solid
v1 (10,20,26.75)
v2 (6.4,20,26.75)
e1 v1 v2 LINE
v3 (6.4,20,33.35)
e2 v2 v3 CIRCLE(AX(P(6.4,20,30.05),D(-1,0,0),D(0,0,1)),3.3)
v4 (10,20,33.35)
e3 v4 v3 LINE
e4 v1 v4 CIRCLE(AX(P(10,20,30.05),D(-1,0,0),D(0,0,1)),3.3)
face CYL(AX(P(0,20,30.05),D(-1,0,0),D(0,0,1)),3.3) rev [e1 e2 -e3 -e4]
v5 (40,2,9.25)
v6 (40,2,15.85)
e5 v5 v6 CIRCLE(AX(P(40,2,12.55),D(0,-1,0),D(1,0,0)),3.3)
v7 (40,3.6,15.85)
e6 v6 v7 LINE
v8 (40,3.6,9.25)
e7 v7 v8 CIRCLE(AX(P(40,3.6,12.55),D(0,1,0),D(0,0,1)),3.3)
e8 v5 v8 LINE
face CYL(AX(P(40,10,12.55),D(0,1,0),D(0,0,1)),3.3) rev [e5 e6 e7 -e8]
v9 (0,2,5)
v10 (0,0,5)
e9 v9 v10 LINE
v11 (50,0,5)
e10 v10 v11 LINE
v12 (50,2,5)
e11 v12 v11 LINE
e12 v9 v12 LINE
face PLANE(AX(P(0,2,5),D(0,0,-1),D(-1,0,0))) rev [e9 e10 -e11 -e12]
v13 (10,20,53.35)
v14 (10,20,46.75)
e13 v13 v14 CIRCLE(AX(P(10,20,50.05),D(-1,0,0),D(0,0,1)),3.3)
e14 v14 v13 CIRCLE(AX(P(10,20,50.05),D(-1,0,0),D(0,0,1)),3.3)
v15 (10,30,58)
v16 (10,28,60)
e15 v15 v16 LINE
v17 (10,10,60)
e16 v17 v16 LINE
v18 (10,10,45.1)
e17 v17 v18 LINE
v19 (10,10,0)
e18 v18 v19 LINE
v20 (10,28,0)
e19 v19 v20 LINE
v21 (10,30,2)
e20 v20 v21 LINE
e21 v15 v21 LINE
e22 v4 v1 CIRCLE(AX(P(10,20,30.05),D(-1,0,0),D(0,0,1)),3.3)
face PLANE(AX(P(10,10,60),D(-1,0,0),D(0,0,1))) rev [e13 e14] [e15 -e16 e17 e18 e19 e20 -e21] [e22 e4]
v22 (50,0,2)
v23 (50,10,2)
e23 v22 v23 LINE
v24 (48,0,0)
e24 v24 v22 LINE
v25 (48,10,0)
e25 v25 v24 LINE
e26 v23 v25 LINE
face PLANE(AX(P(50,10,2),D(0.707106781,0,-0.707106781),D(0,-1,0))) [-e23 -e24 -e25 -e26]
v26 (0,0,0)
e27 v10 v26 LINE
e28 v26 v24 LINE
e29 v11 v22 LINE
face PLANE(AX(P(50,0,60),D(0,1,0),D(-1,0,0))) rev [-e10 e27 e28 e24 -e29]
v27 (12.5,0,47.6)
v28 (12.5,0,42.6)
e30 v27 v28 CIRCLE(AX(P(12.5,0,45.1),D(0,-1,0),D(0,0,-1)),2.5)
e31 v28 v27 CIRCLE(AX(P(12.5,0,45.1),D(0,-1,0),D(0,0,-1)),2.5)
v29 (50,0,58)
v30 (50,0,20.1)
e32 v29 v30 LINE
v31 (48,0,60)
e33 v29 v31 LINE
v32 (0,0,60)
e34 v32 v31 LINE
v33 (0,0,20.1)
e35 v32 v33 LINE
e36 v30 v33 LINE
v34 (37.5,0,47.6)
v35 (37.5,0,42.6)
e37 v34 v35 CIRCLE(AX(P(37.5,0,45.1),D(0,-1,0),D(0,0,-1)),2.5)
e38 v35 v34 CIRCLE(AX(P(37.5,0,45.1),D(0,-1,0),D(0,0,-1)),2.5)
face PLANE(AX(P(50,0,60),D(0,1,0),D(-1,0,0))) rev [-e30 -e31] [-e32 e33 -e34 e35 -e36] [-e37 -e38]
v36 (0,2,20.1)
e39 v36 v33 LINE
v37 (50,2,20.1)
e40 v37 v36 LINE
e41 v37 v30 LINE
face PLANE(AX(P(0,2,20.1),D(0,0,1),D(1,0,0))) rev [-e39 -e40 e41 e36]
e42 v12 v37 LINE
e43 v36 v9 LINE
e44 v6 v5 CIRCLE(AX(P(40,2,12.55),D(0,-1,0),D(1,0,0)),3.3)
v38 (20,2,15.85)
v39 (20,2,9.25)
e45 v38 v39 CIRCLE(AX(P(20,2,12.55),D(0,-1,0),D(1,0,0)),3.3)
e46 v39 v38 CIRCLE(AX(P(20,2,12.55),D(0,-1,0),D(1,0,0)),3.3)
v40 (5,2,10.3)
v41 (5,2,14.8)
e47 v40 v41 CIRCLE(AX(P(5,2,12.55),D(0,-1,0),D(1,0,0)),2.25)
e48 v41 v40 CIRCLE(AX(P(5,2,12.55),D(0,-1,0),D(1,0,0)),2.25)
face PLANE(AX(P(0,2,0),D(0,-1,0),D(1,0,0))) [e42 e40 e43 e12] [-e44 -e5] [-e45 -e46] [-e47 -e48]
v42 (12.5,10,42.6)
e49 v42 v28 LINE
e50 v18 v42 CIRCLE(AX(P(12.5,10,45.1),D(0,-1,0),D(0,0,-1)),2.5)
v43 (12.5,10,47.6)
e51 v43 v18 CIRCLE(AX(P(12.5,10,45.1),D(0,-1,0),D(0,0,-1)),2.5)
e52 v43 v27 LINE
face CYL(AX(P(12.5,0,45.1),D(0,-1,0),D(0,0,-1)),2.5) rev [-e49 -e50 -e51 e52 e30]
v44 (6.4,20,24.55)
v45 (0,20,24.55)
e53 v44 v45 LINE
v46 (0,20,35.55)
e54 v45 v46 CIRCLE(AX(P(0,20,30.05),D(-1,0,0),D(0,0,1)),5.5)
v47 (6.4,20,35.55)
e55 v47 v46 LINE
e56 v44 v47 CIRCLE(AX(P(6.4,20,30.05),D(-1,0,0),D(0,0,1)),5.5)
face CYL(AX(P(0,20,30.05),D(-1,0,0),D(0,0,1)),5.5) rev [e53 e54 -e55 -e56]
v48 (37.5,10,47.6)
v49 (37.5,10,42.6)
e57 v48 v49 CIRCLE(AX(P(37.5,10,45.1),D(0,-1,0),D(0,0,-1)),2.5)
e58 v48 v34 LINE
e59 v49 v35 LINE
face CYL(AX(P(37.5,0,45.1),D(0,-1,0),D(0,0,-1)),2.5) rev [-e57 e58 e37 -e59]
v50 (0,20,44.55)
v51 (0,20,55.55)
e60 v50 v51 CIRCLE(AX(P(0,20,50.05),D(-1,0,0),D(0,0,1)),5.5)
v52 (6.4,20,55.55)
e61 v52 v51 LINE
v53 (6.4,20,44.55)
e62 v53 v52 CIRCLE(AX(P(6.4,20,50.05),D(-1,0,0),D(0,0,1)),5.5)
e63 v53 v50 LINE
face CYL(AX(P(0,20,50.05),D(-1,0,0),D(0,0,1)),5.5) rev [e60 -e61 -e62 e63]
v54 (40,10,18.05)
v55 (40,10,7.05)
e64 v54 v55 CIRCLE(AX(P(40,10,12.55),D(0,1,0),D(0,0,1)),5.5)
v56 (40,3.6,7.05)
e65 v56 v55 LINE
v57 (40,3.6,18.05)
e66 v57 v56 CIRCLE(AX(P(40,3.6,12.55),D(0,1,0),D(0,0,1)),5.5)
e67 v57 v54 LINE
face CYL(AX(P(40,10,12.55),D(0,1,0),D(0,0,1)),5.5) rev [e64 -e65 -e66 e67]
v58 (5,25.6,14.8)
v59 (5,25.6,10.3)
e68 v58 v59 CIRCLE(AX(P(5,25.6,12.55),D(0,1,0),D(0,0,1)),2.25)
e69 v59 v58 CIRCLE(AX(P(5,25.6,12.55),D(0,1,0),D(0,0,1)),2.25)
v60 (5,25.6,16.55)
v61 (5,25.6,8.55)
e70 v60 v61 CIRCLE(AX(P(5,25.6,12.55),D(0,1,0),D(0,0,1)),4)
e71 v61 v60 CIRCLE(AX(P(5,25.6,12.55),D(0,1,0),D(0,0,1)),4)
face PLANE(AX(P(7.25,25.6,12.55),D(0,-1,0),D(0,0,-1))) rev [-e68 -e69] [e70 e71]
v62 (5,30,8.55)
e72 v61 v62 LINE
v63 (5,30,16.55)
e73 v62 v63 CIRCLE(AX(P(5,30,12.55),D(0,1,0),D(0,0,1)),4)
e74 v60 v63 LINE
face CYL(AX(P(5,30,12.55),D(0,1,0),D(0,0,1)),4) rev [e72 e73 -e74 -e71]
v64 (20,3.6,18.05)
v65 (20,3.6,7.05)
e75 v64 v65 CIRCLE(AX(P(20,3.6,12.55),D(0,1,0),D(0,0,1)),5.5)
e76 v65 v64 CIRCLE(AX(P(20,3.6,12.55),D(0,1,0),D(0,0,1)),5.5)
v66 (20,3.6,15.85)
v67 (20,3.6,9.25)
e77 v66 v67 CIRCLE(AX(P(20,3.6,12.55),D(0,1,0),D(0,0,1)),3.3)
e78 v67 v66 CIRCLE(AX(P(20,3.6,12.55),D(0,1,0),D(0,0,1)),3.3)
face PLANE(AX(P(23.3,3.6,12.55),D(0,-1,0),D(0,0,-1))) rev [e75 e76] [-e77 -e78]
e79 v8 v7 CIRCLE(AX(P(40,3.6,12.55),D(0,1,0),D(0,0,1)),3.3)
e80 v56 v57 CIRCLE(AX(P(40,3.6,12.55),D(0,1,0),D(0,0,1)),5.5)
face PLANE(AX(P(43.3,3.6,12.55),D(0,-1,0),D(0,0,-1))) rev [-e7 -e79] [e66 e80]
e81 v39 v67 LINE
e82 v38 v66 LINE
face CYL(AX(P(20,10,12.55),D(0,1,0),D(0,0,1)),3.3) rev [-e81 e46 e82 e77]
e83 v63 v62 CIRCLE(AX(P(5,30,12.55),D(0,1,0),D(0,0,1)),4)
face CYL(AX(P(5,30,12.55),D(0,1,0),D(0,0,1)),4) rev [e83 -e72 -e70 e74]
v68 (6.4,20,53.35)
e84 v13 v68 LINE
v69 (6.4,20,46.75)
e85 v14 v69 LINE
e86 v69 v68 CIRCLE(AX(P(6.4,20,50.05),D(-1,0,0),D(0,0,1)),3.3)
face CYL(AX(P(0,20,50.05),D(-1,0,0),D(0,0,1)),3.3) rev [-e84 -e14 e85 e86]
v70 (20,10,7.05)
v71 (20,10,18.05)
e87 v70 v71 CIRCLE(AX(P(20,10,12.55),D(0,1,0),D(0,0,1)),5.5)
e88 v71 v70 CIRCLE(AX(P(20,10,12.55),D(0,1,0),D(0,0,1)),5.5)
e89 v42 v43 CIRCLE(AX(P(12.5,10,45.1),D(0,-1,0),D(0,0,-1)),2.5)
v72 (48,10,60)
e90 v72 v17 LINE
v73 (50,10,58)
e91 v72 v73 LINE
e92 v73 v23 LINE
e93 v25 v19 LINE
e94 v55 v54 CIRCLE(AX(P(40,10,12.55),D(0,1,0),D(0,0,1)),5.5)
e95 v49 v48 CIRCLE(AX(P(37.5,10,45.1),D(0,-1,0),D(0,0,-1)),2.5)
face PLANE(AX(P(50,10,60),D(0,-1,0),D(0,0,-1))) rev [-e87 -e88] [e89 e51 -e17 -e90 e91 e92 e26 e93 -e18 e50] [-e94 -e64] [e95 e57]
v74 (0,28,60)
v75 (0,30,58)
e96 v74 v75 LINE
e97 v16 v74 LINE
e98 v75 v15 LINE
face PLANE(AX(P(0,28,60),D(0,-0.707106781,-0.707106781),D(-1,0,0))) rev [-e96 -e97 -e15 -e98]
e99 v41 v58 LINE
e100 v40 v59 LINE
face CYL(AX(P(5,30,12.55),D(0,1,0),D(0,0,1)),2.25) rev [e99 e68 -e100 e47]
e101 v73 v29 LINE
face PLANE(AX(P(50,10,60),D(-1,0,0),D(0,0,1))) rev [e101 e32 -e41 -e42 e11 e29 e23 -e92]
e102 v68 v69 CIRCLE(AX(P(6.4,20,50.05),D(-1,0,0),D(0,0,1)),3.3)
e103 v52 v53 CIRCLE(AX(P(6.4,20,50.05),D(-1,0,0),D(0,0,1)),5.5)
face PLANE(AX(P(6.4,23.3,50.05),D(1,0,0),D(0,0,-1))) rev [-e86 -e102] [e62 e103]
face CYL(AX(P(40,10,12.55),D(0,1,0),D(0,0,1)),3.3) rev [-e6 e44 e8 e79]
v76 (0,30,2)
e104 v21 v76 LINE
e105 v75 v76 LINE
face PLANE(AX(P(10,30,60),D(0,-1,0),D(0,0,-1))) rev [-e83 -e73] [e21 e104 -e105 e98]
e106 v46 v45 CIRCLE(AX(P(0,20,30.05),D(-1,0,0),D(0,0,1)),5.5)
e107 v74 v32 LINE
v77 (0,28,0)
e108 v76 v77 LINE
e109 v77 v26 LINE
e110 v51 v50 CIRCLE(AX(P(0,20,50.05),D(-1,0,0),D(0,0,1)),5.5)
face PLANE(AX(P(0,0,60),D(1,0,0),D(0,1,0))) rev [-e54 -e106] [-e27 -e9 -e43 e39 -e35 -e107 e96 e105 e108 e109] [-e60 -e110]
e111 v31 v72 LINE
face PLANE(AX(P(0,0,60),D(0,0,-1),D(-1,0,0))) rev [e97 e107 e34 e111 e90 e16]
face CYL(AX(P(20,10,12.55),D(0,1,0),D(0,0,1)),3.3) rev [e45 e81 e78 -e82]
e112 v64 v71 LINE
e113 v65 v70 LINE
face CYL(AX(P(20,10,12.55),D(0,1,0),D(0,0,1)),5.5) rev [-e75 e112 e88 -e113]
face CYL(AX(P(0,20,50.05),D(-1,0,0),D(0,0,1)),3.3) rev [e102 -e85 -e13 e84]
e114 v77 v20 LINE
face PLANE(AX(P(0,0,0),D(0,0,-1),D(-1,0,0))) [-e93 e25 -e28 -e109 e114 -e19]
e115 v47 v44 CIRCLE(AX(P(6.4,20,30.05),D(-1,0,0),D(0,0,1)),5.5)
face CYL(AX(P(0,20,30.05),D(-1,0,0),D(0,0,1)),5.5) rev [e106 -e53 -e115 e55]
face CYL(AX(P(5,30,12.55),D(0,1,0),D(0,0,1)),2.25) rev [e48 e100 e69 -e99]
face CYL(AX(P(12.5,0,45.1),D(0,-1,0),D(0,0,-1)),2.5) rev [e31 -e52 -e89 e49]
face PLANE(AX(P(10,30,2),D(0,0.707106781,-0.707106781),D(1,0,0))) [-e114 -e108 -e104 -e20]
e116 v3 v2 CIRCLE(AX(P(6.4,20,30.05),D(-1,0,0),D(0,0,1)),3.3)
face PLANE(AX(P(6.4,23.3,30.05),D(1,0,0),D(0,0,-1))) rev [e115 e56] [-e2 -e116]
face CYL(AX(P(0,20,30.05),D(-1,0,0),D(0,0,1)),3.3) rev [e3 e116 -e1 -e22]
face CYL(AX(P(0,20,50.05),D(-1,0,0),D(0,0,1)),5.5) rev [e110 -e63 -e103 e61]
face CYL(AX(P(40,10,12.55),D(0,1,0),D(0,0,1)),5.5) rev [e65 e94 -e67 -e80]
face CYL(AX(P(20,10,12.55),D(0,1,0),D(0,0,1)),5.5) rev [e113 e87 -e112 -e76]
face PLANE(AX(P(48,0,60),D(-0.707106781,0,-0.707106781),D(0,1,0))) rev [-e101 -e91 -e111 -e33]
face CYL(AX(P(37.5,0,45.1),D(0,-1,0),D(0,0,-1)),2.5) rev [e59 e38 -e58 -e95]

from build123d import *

# Parameters (mm, degrees)
EXTRUDE_1_DEPTH              = 60
SKETCH_3_W                   = 50
SKETCH_3_H                   = 15.1
CUT_EXTRUDE_1_DEPTH          = 2
HOLE_WIZARD_M4_1_D           = 4.5
HOLE_WIZARD_M4_1_CBORE_D     = 8
HOLE_WIZARD_M4_1_CBORE_DEPTH = 4.4
HOLE_WIZARD_M6_1_D           = 6.6
HOLE_WIZARD_M6_1_CBORE_D     = 11
HOLE_WIZARD_M6_1_CBORE_DEPTH = 6.4
HOLE_WIZARD_M6_2_D           = 6.6
HOLE_WIZARD_M6_2_CBORE_D     = 11
HOLE_WIZARD_M6_2_CBORE_DEPTH = 6.4
CHAMFER_1_SIZE               = 2
HOLE_WIZARD_M6_1_2_D         = 5
HOLE_WIZARD_M6_1_2_DEPTH     = 17
HOLE_WIZARD_M6_1_2_TIP       = 1.502151548


with BuildPart() as part:
    # 草图2 → 凸台-拉伸1 (new body)
    with BuildSketch(Plane.XY):
        Polygon((50, 0), (0, 0), (0, 30), (10, 30), (10, 10), (50, 10), align=None)
    extrude(amount=EXTRUDE_1_DEPTH)

    # 草图3 → 切除-拉伸1 (cut)
    with BuildSketch(Plane.XZ):
        with Locations((25, 12.55)):
            Rectangle(SKETCH_3_W, SKETCH_3_H)
    extrude(amount=-CUT_EXTRUDE_1_DEPTH, mode=Mode.SUBTRACT)

    # M4 六角凹头螺钉的柱形沉头孔1 (through all)
    with Locations(Plane(origin=(0, 30, 0), x_dir=(1, 0, 0), z_dir=(0, 1, 0))):
        with Locations((5, -12.55)):
            CounterBoreHole(HOLE_WIZARD_M4_1_D / 2, HOLE_WIZARD_M4_1_CBORE_D / 2, HOLE_WIZARD_M4_1_CBORE_DEPTH)

    # Hole Wizard M6 _1 (through all)
    with Locations(Plane(origin=(0, 10, 0), x_dir=(1, 0, 0), z_dir=(0, 1, 0))):
        with Locations((20, -12.55), (40, -12.55)):
            CounterBoreHole(HOLE_WIZARD_M6_1_D / 2, HOLE_WIZARD_M6_1_CBORE_D / 2, HOLE_WIZARD_M6_1_CBORE_DEPTH)

    # M6 六角凹头螺钉的柱形沉头孔2 (through all)
    with Locations(Plane.ZY):
        with Locations((30.05, 20), (50.05, 20)):
            CounterBoreHole(HOLE_WIZARD_M6_2_D / 2, HOLE_WIZARD_M6_2_CBORE_D / 2, HOLE_WIZARD_M6_2_CBORE_DEPTH)

    # 倒角1
    chamfer_1_edges = [part.edges().sort_by_distance(p)[0] for p in [
        (5, 30, 60),
        (50, 5, 60),
        (5, 30, 0),
        (50, 5, 0),
    ]]
    chamfer(chamfer_1_edges, length=CHAMFER_1_SIZE)

    # Hole Wizard M6 _1 2
    with Locations(Plane(origin=(0, 0, 0), x_dir=(-1, 0, 0), z_dir=(0, -1, 0))):
        with Locations((-37.5, -45.1), (-12.5, -45.1)):
            Hole(HOLE_WIZARD_M6_1_2_D / 2, depth=HOLE_WIZARD_M6_1_2_DEPTH)
            with Locations((0, 0, -(HOLE_WIZARD_M6_1_2_DEPTH + HOLE_WIZARD_M6_1_2_TIP / 2))):  # 118° drill point
                Cone(0, HOLE_WIZARD_M6_1_2_D / 2, HOLE_WIZARD_M6_1_2_TIP, mode=Mode.SUBTRACT)


solid = part.part
